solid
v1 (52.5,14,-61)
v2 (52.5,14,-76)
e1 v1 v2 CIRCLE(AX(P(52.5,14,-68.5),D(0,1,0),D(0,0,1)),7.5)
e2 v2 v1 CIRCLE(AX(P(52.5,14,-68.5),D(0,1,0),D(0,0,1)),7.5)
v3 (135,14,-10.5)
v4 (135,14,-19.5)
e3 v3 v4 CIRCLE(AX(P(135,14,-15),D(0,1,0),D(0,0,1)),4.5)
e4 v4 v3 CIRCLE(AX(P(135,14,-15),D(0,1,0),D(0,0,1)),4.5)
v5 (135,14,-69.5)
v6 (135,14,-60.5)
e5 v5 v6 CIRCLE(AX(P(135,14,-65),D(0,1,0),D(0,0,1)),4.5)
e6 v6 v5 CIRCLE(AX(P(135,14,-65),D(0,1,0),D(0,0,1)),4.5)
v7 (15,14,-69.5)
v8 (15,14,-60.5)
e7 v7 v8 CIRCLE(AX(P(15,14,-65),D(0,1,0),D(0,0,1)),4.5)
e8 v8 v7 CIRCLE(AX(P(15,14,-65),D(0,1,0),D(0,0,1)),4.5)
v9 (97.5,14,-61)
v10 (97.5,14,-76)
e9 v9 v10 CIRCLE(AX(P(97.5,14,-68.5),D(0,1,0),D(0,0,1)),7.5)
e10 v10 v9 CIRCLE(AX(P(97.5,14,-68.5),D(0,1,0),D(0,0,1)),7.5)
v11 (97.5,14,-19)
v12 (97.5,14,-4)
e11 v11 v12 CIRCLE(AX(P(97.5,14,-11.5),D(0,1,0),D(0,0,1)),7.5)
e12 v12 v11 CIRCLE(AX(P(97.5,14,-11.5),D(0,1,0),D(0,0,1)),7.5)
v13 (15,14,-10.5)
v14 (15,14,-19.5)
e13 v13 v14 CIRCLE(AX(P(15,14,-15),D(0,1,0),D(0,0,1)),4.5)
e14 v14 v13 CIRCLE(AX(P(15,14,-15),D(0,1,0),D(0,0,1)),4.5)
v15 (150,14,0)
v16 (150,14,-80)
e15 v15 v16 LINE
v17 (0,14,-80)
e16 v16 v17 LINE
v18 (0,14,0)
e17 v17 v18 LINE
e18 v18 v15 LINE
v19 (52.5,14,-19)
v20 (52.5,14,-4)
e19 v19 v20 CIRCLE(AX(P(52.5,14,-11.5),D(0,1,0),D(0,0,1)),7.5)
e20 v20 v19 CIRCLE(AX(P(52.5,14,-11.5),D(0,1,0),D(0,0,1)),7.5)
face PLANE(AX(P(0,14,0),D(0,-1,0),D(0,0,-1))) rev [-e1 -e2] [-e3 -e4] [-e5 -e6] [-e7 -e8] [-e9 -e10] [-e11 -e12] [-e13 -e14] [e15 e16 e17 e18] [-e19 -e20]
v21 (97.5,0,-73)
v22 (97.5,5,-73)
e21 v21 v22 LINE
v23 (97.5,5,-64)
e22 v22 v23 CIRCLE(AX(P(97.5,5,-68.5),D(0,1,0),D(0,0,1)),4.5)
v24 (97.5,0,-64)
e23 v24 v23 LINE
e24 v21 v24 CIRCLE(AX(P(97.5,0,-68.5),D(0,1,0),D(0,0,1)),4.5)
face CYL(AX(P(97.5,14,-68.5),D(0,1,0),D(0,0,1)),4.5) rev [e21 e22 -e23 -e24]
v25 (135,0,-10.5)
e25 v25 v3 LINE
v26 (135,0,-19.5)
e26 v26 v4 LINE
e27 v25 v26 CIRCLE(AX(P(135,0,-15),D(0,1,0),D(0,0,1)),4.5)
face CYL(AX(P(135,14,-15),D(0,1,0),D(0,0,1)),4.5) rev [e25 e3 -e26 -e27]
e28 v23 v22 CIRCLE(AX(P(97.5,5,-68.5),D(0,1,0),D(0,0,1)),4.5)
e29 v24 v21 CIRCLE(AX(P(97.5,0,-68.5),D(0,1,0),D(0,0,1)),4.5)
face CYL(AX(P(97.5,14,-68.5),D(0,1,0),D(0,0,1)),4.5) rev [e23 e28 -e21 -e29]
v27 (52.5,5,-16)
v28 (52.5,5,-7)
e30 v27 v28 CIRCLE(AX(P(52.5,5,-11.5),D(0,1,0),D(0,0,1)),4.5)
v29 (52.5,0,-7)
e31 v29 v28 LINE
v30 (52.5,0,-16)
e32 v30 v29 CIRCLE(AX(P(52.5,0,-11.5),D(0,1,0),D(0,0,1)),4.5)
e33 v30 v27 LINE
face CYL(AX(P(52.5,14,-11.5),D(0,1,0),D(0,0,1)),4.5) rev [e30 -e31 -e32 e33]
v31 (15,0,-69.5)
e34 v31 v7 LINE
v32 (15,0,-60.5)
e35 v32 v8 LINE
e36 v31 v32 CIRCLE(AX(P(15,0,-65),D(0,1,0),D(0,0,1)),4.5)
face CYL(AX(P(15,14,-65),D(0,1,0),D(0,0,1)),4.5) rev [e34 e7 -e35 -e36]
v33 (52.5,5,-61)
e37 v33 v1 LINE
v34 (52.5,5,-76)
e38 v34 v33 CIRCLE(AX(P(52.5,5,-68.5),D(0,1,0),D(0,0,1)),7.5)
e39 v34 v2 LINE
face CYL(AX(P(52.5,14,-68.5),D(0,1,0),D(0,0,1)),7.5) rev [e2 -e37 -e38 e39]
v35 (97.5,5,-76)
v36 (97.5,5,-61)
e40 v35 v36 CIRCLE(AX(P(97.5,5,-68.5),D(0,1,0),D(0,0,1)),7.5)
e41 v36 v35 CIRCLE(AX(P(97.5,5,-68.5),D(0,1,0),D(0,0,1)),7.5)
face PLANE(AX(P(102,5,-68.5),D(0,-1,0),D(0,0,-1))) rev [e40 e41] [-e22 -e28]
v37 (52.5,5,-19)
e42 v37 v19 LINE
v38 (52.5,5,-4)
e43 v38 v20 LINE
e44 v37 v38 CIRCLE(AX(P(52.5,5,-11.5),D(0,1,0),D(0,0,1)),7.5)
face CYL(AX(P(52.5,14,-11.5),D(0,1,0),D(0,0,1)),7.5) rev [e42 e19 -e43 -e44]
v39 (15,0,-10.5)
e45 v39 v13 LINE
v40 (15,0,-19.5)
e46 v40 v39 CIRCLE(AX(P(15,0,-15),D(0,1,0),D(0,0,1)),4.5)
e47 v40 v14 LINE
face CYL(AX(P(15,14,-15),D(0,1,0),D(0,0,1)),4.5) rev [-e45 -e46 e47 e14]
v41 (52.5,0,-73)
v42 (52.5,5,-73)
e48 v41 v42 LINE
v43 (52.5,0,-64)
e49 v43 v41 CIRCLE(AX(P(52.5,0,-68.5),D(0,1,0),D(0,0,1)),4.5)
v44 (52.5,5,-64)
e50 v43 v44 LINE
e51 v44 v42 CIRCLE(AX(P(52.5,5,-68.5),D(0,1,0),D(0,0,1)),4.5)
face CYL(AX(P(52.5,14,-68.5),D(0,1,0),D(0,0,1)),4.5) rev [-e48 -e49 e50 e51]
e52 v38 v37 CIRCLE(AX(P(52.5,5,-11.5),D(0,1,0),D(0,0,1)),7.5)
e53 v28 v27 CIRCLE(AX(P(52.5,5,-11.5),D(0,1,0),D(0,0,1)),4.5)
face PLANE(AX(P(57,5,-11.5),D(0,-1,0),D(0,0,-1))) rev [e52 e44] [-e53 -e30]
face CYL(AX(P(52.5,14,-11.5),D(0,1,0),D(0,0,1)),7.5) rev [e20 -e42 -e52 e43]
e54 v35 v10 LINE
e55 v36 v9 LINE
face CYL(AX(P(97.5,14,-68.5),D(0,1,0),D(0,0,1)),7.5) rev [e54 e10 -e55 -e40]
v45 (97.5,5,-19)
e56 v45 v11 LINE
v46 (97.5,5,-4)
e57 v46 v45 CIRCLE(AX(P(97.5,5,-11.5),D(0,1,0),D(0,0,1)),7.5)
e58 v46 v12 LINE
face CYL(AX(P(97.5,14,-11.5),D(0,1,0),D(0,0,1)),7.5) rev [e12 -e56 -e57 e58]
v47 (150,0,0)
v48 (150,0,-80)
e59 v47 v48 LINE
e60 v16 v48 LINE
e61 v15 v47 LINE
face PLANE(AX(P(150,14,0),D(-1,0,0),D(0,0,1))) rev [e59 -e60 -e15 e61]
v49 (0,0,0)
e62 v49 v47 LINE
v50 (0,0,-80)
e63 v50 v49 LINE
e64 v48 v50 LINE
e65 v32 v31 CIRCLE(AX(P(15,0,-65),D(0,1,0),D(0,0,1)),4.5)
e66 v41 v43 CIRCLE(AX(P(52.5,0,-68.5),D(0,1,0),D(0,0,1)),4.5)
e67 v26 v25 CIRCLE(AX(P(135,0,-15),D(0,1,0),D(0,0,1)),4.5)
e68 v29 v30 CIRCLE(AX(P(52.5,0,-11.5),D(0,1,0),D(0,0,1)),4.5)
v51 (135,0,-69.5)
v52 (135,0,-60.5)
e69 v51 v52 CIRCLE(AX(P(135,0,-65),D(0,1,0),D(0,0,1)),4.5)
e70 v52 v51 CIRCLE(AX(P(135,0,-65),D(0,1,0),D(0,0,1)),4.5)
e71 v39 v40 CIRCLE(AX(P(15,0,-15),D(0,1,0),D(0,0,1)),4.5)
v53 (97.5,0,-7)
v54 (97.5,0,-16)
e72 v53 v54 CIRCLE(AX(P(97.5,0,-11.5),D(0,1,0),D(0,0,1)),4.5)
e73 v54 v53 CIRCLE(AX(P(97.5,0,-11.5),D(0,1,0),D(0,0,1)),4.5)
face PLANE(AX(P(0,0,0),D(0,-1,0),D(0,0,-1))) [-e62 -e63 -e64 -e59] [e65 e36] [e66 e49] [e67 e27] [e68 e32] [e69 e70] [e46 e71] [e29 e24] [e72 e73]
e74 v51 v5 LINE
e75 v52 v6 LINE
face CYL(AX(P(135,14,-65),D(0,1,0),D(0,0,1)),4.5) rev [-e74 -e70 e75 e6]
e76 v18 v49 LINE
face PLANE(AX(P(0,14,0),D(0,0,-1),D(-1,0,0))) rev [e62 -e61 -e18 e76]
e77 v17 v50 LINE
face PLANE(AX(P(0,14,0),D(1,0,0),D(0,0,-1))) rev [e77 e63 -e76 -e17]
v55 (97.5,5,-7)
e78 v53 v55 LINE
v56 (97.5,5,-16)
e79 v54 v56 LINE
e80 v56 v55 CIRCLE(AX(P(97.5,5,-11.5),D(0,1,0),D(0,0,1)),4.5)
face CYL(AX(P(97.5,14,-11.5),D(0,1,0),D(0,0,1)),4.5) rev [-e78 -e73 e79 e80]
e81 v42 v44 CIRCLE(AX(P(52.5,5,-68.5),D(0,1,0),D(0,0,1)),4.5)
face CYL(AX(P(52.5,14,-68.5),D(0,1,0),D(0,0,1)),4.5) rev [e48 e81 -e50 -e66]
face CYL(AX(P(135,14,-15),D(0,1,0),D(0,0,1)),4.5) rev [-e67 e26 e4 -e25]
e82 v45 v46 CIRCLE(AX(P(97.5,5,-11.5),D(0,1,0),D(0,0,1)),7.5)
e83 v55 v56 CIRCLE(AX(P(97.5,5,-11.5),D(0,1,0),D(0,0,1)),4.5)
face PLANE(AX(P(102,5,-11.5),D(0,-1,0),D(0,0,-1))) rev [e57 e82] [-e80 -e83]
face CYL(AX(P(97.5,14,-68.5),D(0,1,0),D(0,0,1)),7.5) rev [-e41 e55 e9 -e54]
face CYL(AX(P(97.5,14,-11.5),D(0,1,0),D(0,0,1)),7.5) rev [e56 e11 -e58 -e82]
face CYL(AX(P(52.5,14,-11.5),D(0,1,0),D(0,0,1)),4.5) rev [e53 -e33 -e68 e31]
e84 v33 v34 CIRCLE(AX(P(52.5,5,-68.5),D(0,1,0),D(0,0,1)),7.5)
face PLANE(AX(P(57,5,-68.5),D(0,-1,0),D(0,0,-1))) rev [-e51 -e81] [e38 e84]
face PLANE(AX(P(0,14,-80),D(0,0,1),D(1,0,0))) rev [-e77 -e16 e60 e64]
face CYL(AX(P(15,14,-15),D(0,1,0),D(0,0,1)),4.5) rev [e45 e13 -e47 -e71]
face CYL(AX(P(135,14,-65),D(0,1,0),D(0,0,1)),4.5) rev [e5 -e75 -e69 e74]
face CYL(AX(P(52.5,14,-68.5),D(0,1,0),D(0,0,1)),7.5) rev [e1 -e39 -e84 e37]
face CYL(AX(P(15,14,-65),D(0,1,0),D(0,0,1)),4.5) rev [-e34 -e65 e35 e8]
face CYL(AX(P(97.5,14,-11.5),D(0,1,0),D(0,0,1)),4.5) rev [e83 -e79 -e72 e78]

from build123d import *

# Parameters (mm, degrees)
SKETCH1_W                                         = 150
SKETCH1_H                                         = 80
BOSS_EXTRUDE1_DEPTH                               = 14
HOLE_SIZE_BY_SOCKET_HEAD_CAP_SCREW_TY_D           = 9
HOLE_SIZE_BY_SOCKET_HEAD_CAP_SCREW_TY_CBORE_D     = 15
HOLE_SIZE_BY_SOCKET_HEAD_CAP_SCREW_TY_CBORE_DEPTH = 9
F_9_0_9_DIAMETER_HOLE1_D                          = 9


with BuildPart() as part:
    # Sketch1 → Boss-Extrude1 (new body)
    with BuildSketch(Plane(origin=(0, 0, 0), x_dir=(1, 0, 0), z_dir=(0, 1, 0))):
        with Locations((75, 40)):
            Rectangle(SKETCH1_W, SKETCH1_H)
    extrude(amount=BOSS_EXTRUDE1_DEPTH)

    # Hole size (% by) socket head cap screw type1 (through all)
    with Locations(Plane(origin=(0, 14, 0), x_dir=(-1, 0, 0), z_dir=(0, 1, 0))):
        with Locations((-52.5, -68.5), (-52.5, -11.5), (-97.5, -11.5), (-97.5, -68.5)):
            CounterBoreHole(HOLE_SIZE_BY_SOCKET_HEAD_CAP_SCREW_TY_D / 2, HOLE_SIZE_BY_SOCKET_HEAD_CAP_SCREW_TY_CBORE_D / 2, HOLE_SIZE_BY_SOCKET_HEAD_CAP_SCREW_TY_CBORE_DEPTH)

    # Ø9.0 (9) Diameter Hole1 (through all)
    with Locations(Plane(origin=(0, 14, 0), x_dir=(-1, 0, 0), z_dir=(0, 1, 0))):
        with Locations((-15, -65), (-15, -15), (-135, -15), (-135, -65)):
            Hole(F_9_0_9_DIAMETER_HOLE1_D / 2)


solid = part.part
